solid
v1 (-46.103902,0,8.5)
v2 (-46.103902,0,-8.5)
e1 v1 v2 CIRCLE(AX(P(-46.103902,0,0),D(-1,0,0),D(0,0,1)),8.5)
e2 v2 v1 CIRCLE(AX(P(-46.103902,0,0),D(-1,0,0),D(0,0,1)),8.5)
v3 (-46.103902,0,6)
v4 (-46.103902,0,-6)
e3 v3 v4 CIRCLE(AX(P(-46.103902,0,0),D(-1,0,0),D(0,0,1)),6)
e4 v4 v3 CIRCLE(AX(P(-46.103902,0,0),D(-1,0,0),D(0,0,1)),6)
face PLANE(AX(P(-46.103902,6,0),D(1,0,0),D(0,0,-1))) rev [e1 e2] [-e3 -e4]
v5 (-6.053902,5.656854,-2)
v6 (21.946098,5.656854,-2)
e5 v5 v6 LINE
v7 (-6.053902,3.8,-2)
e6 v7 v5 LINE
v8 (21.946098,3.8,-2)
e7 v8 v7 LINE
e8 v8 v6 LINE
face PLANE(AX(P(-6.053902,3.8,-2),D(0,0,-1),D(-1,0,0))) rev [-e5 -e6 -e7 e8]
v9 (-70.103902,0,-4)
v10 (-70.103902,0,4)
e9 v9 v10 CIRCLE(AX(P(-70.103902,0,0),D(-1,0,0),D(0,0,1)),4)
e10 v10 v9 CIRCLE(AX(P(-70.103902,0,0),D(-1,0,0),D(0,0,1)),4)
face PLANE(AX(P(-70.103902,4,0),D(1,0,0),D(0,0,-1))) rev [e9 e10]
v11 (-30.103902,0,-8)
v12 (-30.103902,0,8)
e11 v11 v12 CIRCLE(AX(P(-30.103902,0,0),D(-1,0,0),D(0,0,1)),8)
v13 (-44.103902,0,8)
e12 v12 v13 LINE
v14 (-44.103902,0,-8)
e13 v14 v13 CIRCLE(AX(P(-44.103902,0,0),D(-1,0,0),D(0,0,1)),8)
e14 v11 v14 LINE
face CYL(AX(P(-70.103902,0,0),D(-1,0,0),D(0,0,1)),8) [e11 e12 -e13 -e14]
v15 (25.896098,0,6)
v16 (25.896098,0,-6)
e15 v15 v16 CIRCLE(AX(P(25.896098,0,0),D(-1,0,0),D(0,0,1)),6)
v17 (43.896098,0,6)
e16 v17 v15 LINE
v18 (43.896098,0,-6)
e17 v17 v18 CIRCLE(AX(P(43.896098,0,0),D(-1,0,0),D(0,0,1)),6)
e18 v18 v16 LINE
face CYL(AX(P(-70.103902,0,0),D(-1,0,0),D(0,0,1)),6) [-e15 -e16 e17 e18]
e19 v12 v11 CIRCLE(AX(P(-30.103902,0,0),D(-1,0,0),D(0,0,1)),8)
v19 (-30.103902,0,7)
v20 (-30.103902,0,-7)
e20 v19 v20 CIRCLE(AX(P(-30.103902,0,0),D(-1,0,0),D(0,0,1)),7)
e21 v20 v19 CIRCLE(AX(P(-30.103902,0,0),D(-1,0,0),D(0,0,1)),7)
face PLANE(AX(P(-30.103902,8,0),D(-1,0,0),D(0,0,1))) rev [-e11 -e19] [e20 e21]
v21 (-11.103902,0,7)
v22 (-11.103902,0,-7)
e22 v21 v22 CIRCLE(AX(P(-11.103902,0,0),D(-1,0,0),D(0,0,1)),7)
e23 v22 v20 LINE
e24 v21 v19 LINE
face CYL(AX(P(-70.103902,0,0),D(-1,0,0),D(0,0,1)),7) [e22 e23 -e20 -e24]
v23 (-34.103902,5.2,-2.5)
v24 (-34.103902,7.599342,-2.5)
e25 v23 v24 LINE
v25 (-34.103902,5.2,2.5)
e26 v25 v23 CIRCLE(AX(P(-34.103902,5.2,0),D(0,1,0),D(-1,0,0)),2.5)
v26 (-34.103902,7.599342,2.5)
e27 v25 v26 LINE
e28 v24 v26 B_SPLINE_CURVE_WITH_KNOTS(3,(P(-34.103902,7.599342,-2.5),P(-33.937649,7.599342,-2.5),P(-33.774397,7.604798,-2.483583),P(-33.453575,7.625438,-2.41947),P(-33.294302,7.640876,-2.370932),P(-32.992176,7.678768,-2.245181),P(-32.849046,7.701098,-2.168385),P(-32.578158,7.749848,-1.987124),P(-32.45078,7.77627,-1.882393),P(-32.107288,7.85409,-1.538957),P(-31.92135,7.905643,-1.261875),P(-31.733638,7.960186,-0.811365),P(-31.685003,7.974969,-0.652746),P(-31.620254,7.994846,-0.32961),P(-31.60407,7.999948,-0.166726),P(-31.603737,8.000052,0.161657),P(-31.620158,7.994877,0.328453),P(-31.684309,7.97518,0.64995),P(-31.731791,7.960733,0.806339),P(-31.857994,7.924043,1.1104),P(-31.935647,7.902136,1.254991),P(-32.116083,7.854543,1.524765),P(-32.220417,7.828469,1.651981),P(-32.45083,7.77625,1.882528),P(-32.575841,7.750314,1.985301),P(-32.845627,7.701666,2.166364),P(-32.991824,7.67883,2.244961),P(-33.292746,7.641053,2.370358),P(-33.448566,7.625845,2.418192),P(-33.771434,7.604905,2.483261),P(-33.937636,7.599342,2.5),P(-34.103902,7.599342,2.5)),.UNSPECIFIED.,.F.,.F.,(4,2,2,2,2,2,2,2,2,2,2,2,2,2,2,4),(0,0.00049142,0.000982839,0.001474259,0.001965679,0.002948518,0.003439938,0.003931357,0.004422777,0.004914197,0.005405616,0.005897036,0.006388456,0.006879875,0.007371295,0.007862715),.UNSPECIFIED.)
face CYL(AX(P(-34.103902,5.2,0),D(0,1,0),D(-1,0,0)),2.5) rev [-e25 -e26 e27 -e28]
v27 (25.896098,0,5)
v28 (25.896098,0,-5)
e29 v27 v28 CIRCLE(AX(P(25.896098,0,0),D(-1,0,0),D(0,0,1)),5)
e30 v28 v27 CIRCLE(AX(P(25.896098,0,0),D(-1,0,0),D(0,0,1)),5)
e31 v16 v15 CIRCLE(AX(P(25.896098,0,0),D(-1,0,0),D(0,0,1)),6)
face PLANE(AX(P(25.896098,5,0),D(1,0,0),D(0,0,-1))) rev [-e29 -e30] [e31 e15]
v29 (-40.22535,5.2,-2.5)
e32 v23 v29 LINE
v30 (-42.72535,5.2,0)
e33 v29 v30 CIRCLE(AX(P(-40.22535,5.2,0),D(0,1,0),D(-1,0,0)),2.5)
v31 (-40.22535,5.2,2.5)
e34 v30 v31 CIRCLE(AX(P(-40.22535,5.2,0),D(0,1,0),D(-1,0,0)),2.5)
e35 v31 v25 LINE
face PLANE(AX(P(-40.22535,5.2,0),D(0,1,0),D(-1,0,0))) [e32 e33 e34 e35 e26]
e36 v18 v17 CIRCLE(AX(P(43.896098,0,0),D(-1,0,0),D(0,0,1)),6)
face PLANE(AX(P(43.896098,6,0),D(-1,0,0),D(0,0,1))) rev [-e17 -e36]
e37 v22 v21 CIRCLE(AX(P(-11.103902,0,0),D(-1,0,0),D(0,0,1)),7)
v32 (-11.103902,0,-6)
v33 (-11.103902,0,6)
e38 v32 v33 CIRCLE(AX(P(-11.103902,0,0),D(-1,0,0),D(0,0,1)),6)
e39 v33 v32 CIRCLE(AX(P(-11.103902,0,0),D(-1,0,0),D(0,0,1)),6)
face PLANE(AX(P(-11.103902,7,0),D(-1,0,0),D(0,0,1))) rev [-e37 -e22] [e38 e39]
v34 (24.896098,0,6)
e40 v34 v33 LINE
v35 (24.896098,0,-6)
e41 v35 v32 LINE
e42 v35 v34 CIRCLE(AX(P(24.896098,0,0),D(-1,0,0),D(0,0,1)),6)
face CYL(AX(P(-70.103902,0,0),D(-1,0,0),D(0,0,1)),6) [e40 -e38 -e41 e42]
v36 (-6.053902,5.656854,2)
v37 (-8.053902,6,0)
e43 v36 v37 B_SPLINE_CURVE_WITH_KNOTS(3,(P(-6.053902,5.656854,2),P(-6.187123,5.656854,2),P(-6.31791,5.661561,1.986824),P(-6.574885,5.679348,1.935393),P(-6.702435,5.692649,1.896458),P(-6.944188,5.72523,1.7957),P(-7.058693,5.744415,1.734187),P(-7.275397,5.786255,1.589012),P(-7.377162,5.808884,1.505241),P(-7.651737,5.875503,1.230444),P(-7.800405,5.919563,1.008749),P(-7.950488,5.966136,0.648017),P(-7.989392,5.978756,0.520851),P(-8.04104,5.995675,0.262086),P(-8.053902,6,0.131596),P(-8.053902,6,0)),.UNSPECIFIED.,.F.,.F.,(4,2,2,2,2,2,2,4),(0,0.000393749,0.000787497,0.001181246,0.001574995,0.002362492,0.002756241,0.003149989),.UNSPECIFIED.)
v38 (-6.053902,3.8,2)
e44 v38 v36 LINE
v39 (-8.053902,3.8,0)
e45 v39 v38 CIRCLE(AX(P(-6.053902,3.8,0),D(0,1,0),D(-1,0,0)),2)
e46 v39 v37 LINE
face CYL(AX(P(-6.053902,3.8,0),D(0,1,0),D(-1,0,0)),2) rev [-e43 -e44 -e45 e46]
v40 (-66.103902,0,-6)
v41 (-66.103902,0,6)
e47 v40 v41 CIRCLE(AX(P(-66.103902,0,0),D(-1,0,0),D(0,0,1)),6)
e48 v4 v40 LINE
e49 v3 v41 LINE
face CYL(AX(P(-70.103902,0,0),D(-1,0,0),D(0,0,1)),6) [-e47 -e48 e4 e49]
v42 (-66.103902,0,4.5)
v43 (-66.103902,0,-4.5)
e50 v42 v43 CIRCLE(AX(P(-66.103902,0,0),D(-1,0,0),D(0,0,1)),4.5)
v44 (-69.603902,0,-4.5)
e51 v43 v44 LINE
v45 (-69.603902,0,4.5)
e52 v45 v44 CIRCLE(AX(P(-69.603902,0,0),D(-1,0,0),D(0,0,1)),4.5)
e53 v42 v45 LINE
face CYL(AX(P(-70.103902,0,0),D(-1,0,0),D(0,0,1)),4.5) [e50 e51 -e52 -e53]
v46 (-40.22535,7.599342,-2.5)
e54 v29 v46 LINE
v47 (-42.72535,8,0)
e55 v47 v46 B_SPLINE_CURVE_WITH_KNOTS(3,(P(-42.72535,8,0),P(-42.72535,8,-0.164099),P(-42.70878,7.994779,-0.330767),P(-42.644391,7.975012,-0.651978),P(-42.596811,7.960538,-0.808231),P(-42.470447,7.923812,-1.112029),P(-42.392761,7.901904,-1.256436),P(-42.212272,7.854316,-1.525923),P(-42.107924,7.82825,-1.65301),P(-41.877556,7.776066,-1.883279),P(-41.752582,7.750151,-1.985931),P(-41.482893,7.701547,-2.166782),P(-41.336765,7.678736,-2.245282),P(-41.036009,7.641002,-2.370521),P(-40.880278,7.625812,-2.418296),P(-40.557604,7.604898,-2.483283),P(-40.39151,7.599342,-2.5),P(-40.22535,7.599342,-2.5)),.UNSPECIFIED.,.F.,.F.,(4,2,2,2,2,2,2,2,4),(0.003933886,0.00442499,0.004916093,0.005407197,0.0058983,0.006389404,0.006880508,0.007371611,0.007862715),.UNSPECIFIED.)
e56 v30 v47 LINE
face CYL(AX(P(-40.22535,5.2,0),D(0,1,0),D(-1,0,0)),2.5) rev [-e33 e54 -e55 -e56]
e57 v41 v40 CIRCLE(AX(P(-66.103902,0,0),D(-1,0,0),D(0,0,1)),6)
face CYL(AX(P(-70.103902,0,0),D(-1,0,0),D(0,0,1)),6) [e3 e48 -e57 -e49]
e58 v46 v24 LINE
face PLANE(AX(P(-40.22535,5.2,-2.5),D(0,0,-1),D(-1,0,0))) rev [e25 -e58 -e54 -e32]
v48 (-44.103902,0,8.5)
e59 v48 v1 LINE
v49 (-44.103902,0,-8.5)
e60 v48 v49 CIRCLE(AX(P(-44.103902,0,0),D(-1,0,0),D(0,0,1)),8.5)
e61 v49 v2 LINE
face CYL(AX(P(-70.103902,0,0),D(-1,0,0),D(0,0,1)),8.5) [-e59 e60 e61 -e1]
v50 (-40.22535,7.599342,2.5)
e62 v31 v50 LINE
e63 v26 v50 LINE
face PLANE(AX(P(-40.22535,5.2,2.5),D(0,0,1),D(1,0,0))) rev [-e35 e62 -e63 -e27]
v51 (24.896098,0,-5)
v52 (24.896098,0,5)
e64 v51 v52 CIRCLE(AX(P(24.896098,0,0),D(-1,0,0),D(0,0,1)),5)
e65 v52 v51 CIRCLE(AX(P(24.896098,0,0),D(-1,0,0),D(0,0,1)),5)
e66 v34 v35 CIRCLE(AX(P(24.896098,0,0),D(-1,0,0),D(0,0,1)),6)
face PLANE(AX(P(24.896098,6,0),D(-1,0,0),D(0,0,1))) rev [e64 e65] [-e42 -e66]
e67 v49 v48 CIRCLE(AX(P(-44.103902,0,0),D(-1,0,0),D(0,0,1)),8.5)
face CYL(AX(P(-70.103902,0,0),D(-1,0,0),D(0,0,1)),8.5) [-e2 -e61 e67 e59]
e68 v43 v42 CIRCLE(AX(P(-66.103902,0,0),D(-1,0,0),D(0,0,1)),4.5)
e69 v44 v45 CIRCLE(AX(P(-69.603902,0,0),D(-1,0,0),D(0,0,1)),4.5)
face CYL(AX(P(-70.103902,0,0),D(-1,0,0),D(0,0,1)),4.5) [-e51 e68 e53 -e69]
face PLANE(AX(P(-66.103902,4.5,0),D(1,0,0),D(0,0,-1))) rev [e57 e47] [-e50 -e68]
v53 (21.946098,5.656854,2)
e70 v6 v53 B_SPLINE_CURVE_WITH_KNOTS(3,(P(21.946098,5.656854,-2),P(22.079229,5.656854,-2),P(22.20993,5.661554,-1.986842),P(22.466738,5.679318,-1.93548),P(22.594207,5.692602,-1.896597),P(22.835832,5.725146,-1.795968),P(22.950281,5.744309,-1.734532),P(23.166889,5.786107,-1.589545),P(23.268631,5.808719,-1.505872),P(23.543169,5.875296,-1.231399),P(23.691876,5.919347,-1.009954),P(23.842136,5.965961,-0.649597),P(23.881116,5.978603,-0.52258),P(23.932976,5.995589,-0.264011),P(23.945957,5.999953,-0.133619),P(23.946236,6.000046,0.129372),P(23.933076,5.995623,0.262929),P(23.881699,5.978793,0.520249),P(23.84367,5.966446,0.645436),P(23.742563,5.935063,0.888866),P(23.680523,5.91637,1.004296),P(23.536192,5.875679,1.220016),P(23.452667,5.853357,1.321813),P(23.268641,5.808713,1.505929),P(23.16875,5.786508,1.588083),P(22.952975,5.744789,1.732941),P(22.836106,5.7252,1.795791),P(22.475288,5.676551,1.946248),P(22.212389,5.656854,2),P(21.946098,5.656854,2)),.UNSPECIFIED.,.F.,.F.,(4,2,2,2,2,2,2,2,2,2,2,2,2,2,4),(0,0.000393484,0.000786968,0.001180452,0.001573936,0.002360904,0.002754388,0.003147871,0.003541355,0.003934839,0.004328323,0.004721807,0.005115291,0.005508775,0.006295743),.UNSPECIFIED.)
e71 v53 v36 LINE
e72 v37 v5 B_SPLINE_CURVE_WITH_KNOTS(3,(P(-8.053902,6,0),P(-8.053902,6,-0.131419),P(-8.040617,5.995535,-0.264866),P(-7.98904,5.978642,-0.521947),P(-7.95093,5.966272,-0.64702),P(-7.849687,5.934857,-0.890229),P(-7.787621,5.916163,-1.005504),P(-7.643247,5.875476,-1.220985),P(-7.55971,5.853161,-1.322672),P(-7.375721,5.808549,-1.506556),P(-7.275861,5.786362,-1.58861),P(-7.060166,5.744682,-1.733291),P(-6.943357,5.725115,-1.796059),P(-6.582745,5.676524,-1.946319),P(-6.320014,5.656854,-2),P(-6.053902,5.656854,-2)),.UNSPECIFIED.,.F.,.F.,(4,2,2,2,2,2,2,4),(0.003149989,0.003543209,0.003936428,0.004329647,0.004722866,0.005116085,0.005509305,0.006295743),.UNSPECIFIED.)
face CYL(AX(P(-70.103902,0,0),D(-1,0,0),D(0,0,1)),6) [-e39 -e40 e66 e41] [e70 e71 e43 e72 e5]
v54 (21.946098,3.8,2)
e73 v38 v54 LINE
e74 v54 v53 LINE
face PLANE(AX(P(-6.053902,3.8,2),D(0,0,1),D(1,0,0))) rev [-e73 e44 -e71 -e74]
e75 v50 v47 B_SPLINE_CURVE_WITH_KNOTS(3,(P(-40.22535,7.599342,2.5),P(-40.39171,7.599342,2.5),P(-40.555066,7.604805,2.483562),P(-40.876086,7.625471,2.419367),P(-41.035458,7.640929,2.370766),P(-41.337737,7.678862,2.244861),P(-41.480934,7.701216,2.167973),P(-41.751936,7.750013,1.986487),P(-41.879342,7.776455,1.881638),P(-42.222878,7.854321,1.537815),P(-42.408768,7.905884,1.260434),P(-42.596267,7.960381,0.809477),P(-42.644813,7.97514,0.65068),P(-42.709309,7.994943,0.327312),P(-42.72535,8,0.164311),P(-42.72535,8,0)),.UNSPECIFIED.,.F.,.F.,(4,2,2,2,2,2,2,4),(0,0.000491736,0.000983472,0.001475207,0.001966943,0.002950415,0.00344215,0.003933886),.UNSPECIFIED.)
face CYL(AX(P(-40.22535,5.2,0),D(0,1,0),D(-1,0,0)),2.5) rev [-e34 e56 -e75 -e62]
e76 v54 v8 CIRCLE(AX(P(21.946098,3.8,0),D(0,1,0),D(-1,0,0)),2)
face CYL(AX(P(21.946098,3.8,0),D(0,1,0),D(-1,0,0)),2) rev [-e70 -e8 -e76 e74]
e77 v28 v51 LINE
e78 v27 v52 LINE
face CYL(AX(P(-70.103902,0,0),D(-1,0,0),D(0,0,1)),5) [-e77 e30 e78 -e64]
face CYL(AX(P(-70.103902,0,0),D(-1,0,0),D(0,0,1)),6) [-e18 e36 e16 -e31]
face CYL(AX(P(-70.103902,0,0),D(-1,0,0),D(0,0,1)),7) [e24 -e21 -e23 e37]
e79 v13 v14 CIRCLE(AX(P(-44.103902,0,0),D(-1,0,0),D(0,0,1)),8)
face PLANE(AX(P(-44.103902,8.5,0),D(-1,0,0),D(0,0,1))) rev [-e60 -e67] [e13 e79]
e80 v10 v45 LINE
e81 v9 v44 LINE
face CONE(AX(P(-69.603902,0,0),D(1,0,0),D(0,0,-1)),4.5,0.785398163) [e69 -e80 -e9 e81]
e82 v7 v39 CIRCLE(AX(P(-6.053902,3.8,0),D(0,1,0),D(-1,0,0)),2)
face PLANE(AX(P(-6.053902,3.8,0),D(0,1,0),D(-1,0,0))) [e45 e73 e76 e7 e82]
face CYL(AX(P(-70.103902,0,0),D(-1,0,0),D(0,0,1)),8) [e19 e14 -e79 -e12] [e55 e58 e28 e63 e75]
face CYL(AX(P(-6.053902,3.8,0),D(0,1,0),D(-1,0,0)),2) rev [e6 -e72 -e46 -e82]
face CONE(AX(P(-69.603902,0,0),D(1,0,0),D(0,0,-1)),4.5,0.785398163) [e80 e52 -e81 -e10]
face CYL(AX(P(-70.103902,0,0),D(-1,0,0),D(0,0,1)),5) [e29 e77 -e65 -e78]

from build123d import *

# Parameters (mm, degrees)
CUT_EXTRUDE_1_DEPTH = 2.2
CUT_EXTRUDE_2_DEPTH = 2.8


with BuildPart() as part:
    # 草图1 → 旋转1 (revolve)
    with BuildSketch(Plane.XY, mode=Mode.PRIVATE) as revolve_1_sk:
        Polygon((-46.103902345, 8.5), (-44.103902345, 8.5), (-44.103902345, 8), (-30.103902345, 8), (-30.103902345, 7), (-11.103902345, 7), (-11.103902345, 6), (24.896097655, 6), (24.896097655, 5), (25.896097655, 5), (25.896097655, 6), (43.896097655, 6), (43.896097655, 0), (-70.103902345, 0), (-70.103902345, 4), (-69.603902345, 4.5), (-66.103902345, 4.5), (-66.103902345, 6), (-46.103902345, 6), align=None)
    revolve(revolve_1_sk.sketch.rotate(Axis((-70.103902345, 0, 0), (1, 0, 0)), 90), axis=Axis((-70.103902345, 0, 0), (1, 0, 0)))

    # 草图7 → 切除-拉伸1 (cut)
    with BuildSketch(Plane(origin=(0, 6, 0), x_dir=(1, 0, 0), z_dir=(0, 1, 0))):
        with BuildLine():
            Line((-6.053902345, 2), (21.946097655, 2))
            ThreePointArc((21.946097655, 2), (23.946097655, 0), (21.946097655, -2))
            Line((21.946097655, -2), (-6.053902345, -2))
            ThreePointArc((-6.053902345, -2), (-8.053902345, 0), (-6.053902345, 2))
        make_face()
    extrude(amount=-CUT_EXTRUDE_1_DEPTH, mode=Mode.SUBTRACT)

    # 草图9 → 切除-拉伸2 (cut)
    with BuildSketch(Plane(origin=(0, 8, 0), x_dir=(1, 0, 0), z_dir=(0, 1, 0))):
        with BuildLine():
            Line((-40.225350305, 2.5), (-34.103902345, 2.5))
            ThreePointArc((-34.103902345, 2.5), (-31.603902345, 0), (-34.103902345, -2.5))
            Line((-34.103902345, -2.5), (-40.225350305, -2.5))
            ThreePointArc((-40.225350305, -2.5), (-42.725350305, 0), (-40.225350305, 2.5))
        make_face()
    extrude(amount=-CUT_EXTRUDE_2_DEPTH, mode=Mode.SUBTRACT)


solid = part.part
